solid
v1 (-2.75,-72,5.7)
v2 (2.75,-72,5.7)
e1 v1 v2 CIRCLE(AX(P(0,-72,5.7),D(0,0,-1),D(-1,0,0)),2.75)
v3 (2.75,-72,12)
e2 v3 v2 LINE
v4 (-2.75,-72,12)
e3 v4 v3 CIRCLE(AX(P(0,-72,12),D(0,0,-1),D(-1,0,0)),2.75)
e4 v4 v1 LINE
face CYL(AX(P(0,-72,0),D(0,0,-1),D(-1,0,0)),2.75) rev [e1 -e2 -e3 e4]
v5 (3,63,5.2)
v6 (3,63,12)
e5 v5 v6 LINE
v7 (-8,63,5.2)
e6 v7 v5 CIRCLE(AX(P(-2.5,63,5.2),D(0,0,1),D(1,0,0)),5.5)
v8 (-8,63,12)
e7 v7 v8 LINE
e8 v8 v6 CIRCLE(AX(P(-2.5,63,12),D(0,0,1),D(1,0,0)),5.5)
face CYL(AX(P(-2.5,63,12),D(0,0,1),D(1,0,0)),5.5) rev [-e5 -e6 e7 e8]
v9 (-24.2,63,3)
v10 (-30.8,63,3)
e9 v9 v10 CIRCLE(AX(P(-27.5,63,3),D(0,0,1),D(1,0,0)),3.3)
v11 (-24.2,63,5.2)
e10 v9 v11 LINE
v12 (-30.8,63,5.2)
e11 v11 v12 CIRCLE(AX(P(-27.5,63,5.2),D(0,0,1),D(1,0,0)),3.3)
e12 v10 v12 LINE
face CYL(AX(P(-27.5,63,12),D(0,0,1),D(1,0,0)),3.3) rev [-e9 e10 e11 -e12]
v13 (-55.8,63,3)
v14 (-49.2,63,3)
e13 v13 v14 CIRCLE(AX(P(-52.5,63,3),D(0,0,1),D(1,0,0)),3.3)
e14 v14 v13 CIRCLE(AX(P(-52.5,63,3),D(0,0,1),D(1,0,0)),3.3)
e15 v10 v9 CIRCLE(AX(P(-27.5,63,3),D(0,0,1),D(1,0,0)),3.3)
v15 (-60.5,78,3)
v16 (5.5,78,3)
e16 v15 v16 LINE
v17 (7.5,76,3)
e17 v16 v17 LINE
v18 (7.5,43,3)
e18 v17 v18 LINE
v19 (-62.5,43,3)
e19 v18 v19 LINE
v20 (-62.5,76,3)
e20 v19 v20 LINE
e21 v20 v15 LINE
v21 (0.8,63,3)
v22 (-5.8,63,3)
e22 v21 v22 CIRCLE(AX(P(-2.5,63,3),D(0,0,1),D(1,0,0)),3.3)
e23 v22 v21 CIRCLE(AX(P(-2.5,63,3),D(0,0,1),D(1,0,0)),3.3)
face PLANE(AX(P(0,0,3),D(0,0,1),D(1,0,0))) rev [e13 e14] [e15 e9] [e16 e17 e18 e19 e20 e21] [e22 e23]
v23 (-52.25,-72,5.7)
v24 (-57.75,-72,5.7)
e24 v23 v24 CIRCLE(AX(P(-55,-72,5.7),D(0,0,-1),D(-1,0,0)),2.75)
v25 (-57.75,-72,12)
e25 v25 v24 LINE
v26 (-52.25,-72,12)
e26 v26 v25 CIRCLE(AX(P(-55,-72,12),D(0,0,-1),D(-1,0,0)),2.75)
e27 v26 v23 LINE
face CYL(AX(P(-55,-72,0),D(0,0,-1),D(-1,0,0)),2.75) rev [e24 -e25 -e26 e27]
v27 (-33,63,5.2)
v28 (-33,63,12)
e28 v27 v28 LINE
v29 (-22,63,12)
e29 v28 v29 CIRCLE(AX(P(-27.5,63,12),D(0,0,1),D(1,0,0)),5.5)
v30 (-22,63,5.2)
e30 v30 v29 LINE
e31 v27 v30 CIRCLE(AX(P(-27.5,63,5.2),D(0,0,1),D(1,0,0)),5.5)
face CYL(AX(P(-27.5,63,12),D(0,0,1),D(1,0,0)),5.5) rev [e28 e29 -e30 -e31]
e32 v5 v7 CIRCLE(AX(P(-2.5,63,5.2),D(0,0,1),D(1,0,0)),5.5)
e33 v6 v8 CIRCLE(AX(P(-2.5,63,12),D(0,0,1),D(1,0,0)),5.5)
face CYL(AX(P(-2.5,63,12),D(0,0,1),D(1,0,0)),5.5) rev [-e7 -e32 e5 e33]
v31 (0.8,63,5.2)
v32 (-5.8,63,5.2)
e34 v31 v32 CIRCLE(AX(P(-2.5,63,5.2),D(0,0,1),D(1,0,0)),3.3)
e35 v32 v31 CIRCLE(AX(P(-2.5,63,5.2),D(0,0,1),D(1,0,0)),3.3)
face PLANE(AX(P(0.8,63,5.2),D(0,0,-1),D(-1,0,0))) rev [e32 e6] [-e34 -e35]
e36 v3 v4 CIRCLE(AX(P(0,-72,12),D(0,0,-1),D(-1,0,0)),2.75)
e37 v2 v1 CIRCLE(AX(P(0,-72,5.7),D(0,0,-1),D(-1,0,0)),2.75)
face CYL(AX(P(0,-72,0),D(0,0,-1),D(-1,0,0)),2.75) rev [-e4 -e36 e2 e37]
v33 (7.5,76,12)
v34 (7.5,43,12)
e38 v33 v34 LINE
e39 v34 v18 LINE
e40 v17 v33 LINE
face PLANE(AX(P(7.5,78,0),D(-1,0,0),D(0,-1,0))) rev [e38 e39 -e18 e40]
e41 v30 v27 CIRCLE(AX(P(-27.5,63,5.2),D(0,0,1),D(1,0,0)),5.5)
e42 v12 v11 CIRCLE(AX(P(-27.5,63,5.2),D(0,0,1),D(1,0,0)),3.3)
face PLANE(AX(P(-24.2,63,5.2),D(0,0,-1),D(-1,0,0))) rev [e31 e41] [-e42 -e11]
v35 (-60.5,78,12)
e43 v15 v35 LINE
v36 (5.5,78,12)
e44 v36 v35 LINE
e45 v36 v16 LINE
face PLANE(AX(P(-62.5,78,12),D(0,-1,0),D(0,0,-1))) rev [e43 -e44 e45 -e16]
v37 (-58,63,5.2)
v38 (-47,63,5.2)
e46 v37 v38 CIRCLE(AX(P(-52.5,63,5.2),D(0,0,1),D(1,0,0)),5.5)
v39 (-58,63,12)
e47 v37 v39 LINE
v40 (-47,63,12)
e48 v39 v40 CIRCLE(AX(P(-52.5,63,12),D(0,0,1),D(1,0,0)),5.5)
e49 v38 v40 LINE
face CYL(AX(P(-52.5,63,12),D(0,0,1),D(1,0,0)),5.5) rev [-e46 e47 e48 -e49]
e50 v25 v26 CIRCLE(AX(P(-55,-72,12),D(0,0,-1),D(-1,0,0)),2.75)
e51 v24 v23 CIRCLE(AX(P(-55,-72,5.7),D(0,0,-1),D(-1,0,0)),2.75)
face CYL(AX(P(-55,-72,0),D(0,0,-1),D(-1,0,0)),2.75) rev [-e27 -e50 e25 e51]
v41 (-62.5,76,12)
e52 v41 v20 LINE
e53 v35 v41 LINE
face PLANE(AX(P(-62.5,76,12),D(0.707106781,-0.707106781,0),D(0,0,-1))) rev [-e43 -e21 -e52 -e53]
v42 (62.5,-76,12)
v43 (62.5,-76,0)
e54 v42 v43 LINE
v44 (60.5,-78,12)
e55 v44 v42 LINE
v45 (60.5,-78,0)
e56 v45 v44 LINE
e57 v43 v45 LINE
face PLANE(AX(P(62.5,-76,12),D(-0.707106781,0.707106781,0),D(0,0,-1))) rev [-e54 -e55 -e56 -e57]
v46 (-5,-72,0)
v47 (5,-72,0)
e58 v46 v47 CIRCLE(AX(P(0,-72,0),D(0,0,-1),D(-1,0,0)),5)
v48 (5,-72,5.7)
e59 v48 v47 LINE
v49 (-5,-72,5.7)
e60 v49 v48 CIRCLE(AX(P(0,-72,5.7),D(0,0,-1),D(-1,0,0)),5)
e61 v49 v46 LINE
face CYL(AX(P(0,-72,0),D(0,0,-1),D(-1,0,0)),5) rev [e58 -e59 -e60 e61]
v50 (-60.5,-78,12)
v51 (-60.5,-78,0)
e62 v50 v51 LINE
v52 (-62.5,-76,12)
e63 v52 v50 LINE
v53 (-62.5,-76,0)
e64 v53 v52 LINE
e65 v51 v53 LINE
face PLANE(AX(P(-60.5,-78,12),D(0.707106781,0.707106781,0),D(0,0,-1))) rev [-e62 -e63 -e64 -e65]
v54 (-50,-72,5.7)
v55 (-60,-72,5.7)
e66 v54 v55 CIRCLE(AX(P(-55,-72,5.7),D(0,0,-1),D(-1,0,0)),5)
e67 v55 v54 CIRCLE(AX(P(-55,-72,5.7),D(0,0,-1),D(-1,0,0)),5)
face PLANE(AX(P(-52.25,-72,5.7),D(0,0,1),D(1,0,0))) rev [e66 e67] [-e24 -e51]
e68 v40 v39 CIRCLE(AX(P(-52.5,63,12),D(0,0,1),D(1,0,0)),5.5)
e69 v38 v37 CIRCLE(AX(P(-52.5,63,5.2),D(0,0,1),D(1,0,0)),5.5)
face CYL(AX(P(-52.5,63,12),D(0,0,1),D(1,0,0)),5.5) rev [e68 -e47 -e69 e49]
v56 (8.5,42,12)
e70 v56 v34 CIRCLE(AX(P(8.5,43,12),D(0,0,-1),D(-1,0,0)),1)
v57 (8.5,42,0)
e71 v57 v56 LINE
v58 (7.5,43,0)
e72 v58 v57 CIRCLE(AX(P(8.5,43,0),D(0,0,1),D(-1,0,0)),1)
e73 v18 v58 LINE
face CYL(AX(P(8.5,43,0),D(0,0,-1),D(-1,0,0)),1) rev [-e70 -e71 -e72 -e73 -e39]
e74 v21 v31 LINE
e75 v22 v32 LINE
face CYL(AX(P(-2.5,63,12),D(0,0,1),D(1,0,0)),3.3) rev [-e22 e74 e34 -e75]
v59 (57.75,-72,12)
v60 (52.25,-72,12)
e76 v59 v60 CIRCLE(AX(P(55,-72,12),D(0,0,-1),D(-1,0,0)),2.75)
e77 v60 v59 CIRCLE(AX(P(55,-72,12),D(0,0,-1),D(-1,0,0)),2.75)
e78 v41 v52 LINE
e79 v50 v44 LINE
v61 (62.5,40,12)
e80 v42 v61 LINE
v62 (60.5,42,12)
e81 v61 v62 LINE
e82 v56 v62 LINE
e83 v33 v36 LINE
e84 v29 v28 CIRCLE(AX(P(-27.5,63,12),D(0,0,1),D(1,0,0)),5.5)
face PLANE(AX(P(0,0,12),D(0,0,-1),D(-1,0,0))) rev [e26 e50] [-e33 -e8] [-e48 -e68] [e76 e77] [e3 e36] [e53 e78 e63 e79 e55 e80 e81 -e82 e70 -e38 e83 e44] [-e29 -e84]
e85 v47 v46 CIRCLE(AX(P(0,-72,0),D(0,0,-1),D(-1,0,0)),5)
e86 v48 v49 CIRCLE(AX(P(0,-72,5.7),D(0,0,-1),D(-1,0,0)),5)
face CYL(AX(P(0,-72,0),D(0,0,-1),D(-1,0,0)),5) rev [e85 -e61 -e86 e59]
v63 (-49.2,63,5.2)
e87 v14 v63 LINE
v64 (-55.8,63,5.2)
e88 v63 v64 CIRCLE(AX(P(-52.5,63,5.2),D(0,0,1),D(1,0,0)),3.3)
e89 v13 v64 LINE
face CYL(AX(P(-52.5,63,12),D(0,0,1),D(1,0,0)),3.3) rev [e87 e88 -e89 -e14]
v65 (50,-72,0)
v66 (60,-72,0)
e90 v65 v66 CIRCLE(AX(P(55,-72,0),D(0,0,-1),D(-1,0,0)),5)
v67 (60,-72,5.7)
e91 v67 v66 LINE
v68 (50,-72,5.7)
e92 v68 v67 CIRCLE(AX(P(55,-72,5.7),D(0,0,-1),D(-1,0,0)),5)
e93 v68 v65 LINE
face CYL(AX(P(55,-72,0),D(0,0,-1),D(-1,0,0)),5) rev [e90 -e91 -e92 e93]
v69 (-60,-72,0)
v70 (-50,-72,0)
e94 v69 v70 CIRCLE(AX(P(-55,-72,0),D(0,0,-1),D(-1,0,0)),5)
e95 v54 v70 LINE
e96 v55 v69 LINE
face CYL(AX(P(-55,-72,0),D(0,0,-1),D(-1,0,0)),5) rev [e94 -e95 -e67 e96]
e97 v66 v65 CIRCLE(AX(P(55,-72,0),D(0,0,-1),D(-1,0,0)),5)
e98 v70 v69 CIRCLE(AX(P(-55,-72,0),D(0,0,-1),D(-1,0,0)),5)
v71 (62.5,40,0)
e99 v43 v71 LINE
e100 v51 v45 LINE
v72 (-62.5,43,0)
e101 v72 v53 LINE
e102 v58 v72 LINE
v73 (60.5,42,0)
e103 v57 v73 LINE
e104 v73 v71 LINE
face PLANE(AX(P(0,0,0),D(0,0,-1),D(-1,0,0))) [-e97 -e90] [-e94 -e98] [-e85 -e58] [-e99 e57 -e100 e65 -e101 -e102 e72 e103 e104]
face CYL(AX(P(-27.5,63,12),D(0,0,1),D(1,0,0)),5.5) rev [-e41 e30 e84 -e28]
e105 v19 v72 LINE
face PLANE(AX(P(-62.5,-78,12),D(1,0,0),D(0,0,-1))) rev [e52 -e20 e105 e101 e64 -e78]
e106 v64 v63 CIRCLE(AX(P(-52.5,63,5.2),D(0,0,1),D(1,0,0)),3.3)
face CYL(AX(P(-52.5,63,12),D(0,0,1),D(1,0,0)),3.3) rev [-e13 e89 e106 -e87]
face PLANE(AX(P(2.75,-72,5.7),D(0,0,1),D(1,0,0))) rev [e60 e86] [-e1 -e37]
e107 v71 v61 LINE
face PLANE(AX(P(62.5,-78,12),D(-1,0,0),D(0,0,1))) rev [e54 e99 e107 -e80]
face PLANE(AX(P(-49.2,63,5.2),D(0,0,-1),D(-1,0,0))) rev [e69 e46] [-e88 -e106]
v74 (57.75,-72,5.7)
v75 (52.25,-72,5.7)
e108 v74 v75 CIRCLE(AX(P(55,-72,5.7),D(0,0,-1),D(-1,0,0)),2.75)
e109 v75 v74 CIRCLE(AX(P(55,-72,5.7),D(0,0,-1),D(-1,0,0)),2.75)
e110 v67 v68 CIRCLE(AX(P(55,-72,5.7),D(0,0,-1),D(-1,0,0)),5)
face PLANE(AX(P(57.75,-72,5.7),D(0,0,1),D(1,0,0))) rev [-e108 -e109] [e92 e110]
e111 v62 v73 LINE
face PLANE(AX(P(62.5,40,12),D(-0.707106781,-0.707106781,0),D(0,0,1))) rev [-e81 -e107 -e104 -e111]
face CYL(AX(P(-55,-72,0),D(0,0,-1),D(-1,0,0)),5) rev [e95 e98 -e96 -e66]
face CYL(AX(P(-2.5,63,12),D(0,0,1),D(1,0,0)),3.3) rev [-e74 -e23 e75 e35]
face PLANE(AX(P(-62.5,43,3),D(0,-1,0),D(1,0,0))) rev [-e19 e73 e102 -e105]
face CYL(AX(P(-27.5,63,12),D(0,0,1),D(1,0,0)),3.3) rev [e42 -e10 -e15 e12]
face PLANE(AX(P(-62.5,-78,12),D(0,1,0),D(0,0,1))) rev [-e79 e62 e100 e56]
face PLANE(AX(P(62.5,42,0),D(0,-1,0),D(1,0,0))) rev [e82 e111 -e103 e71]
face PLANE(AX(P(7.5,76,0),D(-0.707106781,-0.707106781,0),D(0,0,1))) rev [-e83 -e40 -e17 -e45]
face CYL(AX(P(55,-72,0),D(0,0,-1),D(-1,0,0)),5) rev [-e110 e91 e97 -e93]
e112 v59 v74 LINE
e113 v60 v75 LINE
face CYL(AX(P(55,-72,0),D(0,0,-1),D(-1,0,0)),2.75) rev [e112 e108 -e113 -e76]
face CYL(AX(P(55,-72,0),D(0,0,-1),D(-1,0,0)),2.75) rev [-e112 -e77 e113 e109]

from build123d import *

# Parameters (mm, degrees)
SKETCH_1_W                = 125
SKETCH_1_H                = 156
EXTRUDE_1_DEPTH           = 12
SKETCH_2_W                = 55
SKETCH_2_H                = 36
CUT_EXTRUDE_1_DEPTH       = 101.669012114
SKETCH_3_W                = 70
SKETCH_3_H                = 35
CUT_EXTRUDE_2_DEPTH       = 3
HOLE_WIZARD_1_D           = 5.5
HOLE_WIZARD_1_CBORE_D     = 10
HOLE_WIZARD_1_CBORE_DEPTH = 5.7
HOLE_WIZARD_2_D           = 6.6
HOLE_WIZARD_2_CBORE_D     = 11
HOLE_WIZARD_2_CBORE_DEPTH = 6.8
CHAMFER_1_SIZE            = 2
FILLET_1_R                = 1


with BuildPart() as part:
    # 草图1 → 凸台-拉伸1 (new body)
    with BuildSketch(Plane.XY):
        Rectangle(SKETCH_1_W, SKETCH_1_H)
    extrude(amount=EXTRUDE_1_DEPTH)

    # 草图2 → 切除-拉伸1 (cut, through all)
    with BuildSketch(Plane.XY.offset(12)):
        with Locations((35, 60)):
            Rectangle(SKETCH_2_W, SKETCH_2_H)
    extrude(amount=-CUT_EXTRUDE_1_DEPTH, mode=Mode.SUBTRACT)

    # 草图3 → 切除-拉伸2 (cut)
    with BuildSketch(Plane(origin=(0, 0, 0), x_dir=(-1, 0, 0), z_dir=(0, 0, -1))):
        with Locations((27.5, 60.5)):
            Rectangle(SKETCH_3_W, SKETCH_3_H)
    extrude(amount=-CUT_EXTRUDE_2_DEPTH, mode=Mode.SUBTRACT)

    # 打孔尺寸(%根据)内六角圆柱头螺钉的类型1 (through all)
    with Locations(Plane(origin=(0, 0, 0), x_dir=(-1, 0, 0), z_dir=(0, 0, -1))):
        with Locations((-55, -72), (0, -72), (55, -72)):
            CounterBoreHole(HOLE_WIZARD_1_D / 2, HOLE_WIZARD_1_CBORE_D / 2, HOLE_WIZARD_1_CBORE_DEPTH)

    # 打孔尺寸(%根据)内六角圆柱头螺钉的类型2 (through all)
    with Locations(Plane(origin=(0, 0, 12), x_dir=(-1, 0, 0), z_dir=(0, 0, 1))):
        with Locations((2.5, -63), (27.5, -63), (52.5, -63)):
            CounterBoreHole(HOLE_WIZARD_2_D / 2, HOLE_WIZARD_2_CBORE_D / 2, HOLE_WIZARD_2_CBORE_DEPTH)

    # 倒角1
    chamfer_1_edges = [part.edges().sort_by_distance(p)[0] for p in [
        (62.5, 42, 6),
        (7.5, 78, 7.5),
        (62.5, -78, 6),
        (-62.5, -78, 6),
        (-62.5, 78, 7.5),
    ]]
    chamfer(chamfer_1_edges, length=CHAMFER_1_SIZE)

    # 圆角1
    fillet_1_edges = [part.edges().sort_by_distance(p)[0] for p in [
        (7.5, 42, 6),
    ]]
    fillet(fillet_1_edges, radius=FILLET_1_R)


solid = part.part
